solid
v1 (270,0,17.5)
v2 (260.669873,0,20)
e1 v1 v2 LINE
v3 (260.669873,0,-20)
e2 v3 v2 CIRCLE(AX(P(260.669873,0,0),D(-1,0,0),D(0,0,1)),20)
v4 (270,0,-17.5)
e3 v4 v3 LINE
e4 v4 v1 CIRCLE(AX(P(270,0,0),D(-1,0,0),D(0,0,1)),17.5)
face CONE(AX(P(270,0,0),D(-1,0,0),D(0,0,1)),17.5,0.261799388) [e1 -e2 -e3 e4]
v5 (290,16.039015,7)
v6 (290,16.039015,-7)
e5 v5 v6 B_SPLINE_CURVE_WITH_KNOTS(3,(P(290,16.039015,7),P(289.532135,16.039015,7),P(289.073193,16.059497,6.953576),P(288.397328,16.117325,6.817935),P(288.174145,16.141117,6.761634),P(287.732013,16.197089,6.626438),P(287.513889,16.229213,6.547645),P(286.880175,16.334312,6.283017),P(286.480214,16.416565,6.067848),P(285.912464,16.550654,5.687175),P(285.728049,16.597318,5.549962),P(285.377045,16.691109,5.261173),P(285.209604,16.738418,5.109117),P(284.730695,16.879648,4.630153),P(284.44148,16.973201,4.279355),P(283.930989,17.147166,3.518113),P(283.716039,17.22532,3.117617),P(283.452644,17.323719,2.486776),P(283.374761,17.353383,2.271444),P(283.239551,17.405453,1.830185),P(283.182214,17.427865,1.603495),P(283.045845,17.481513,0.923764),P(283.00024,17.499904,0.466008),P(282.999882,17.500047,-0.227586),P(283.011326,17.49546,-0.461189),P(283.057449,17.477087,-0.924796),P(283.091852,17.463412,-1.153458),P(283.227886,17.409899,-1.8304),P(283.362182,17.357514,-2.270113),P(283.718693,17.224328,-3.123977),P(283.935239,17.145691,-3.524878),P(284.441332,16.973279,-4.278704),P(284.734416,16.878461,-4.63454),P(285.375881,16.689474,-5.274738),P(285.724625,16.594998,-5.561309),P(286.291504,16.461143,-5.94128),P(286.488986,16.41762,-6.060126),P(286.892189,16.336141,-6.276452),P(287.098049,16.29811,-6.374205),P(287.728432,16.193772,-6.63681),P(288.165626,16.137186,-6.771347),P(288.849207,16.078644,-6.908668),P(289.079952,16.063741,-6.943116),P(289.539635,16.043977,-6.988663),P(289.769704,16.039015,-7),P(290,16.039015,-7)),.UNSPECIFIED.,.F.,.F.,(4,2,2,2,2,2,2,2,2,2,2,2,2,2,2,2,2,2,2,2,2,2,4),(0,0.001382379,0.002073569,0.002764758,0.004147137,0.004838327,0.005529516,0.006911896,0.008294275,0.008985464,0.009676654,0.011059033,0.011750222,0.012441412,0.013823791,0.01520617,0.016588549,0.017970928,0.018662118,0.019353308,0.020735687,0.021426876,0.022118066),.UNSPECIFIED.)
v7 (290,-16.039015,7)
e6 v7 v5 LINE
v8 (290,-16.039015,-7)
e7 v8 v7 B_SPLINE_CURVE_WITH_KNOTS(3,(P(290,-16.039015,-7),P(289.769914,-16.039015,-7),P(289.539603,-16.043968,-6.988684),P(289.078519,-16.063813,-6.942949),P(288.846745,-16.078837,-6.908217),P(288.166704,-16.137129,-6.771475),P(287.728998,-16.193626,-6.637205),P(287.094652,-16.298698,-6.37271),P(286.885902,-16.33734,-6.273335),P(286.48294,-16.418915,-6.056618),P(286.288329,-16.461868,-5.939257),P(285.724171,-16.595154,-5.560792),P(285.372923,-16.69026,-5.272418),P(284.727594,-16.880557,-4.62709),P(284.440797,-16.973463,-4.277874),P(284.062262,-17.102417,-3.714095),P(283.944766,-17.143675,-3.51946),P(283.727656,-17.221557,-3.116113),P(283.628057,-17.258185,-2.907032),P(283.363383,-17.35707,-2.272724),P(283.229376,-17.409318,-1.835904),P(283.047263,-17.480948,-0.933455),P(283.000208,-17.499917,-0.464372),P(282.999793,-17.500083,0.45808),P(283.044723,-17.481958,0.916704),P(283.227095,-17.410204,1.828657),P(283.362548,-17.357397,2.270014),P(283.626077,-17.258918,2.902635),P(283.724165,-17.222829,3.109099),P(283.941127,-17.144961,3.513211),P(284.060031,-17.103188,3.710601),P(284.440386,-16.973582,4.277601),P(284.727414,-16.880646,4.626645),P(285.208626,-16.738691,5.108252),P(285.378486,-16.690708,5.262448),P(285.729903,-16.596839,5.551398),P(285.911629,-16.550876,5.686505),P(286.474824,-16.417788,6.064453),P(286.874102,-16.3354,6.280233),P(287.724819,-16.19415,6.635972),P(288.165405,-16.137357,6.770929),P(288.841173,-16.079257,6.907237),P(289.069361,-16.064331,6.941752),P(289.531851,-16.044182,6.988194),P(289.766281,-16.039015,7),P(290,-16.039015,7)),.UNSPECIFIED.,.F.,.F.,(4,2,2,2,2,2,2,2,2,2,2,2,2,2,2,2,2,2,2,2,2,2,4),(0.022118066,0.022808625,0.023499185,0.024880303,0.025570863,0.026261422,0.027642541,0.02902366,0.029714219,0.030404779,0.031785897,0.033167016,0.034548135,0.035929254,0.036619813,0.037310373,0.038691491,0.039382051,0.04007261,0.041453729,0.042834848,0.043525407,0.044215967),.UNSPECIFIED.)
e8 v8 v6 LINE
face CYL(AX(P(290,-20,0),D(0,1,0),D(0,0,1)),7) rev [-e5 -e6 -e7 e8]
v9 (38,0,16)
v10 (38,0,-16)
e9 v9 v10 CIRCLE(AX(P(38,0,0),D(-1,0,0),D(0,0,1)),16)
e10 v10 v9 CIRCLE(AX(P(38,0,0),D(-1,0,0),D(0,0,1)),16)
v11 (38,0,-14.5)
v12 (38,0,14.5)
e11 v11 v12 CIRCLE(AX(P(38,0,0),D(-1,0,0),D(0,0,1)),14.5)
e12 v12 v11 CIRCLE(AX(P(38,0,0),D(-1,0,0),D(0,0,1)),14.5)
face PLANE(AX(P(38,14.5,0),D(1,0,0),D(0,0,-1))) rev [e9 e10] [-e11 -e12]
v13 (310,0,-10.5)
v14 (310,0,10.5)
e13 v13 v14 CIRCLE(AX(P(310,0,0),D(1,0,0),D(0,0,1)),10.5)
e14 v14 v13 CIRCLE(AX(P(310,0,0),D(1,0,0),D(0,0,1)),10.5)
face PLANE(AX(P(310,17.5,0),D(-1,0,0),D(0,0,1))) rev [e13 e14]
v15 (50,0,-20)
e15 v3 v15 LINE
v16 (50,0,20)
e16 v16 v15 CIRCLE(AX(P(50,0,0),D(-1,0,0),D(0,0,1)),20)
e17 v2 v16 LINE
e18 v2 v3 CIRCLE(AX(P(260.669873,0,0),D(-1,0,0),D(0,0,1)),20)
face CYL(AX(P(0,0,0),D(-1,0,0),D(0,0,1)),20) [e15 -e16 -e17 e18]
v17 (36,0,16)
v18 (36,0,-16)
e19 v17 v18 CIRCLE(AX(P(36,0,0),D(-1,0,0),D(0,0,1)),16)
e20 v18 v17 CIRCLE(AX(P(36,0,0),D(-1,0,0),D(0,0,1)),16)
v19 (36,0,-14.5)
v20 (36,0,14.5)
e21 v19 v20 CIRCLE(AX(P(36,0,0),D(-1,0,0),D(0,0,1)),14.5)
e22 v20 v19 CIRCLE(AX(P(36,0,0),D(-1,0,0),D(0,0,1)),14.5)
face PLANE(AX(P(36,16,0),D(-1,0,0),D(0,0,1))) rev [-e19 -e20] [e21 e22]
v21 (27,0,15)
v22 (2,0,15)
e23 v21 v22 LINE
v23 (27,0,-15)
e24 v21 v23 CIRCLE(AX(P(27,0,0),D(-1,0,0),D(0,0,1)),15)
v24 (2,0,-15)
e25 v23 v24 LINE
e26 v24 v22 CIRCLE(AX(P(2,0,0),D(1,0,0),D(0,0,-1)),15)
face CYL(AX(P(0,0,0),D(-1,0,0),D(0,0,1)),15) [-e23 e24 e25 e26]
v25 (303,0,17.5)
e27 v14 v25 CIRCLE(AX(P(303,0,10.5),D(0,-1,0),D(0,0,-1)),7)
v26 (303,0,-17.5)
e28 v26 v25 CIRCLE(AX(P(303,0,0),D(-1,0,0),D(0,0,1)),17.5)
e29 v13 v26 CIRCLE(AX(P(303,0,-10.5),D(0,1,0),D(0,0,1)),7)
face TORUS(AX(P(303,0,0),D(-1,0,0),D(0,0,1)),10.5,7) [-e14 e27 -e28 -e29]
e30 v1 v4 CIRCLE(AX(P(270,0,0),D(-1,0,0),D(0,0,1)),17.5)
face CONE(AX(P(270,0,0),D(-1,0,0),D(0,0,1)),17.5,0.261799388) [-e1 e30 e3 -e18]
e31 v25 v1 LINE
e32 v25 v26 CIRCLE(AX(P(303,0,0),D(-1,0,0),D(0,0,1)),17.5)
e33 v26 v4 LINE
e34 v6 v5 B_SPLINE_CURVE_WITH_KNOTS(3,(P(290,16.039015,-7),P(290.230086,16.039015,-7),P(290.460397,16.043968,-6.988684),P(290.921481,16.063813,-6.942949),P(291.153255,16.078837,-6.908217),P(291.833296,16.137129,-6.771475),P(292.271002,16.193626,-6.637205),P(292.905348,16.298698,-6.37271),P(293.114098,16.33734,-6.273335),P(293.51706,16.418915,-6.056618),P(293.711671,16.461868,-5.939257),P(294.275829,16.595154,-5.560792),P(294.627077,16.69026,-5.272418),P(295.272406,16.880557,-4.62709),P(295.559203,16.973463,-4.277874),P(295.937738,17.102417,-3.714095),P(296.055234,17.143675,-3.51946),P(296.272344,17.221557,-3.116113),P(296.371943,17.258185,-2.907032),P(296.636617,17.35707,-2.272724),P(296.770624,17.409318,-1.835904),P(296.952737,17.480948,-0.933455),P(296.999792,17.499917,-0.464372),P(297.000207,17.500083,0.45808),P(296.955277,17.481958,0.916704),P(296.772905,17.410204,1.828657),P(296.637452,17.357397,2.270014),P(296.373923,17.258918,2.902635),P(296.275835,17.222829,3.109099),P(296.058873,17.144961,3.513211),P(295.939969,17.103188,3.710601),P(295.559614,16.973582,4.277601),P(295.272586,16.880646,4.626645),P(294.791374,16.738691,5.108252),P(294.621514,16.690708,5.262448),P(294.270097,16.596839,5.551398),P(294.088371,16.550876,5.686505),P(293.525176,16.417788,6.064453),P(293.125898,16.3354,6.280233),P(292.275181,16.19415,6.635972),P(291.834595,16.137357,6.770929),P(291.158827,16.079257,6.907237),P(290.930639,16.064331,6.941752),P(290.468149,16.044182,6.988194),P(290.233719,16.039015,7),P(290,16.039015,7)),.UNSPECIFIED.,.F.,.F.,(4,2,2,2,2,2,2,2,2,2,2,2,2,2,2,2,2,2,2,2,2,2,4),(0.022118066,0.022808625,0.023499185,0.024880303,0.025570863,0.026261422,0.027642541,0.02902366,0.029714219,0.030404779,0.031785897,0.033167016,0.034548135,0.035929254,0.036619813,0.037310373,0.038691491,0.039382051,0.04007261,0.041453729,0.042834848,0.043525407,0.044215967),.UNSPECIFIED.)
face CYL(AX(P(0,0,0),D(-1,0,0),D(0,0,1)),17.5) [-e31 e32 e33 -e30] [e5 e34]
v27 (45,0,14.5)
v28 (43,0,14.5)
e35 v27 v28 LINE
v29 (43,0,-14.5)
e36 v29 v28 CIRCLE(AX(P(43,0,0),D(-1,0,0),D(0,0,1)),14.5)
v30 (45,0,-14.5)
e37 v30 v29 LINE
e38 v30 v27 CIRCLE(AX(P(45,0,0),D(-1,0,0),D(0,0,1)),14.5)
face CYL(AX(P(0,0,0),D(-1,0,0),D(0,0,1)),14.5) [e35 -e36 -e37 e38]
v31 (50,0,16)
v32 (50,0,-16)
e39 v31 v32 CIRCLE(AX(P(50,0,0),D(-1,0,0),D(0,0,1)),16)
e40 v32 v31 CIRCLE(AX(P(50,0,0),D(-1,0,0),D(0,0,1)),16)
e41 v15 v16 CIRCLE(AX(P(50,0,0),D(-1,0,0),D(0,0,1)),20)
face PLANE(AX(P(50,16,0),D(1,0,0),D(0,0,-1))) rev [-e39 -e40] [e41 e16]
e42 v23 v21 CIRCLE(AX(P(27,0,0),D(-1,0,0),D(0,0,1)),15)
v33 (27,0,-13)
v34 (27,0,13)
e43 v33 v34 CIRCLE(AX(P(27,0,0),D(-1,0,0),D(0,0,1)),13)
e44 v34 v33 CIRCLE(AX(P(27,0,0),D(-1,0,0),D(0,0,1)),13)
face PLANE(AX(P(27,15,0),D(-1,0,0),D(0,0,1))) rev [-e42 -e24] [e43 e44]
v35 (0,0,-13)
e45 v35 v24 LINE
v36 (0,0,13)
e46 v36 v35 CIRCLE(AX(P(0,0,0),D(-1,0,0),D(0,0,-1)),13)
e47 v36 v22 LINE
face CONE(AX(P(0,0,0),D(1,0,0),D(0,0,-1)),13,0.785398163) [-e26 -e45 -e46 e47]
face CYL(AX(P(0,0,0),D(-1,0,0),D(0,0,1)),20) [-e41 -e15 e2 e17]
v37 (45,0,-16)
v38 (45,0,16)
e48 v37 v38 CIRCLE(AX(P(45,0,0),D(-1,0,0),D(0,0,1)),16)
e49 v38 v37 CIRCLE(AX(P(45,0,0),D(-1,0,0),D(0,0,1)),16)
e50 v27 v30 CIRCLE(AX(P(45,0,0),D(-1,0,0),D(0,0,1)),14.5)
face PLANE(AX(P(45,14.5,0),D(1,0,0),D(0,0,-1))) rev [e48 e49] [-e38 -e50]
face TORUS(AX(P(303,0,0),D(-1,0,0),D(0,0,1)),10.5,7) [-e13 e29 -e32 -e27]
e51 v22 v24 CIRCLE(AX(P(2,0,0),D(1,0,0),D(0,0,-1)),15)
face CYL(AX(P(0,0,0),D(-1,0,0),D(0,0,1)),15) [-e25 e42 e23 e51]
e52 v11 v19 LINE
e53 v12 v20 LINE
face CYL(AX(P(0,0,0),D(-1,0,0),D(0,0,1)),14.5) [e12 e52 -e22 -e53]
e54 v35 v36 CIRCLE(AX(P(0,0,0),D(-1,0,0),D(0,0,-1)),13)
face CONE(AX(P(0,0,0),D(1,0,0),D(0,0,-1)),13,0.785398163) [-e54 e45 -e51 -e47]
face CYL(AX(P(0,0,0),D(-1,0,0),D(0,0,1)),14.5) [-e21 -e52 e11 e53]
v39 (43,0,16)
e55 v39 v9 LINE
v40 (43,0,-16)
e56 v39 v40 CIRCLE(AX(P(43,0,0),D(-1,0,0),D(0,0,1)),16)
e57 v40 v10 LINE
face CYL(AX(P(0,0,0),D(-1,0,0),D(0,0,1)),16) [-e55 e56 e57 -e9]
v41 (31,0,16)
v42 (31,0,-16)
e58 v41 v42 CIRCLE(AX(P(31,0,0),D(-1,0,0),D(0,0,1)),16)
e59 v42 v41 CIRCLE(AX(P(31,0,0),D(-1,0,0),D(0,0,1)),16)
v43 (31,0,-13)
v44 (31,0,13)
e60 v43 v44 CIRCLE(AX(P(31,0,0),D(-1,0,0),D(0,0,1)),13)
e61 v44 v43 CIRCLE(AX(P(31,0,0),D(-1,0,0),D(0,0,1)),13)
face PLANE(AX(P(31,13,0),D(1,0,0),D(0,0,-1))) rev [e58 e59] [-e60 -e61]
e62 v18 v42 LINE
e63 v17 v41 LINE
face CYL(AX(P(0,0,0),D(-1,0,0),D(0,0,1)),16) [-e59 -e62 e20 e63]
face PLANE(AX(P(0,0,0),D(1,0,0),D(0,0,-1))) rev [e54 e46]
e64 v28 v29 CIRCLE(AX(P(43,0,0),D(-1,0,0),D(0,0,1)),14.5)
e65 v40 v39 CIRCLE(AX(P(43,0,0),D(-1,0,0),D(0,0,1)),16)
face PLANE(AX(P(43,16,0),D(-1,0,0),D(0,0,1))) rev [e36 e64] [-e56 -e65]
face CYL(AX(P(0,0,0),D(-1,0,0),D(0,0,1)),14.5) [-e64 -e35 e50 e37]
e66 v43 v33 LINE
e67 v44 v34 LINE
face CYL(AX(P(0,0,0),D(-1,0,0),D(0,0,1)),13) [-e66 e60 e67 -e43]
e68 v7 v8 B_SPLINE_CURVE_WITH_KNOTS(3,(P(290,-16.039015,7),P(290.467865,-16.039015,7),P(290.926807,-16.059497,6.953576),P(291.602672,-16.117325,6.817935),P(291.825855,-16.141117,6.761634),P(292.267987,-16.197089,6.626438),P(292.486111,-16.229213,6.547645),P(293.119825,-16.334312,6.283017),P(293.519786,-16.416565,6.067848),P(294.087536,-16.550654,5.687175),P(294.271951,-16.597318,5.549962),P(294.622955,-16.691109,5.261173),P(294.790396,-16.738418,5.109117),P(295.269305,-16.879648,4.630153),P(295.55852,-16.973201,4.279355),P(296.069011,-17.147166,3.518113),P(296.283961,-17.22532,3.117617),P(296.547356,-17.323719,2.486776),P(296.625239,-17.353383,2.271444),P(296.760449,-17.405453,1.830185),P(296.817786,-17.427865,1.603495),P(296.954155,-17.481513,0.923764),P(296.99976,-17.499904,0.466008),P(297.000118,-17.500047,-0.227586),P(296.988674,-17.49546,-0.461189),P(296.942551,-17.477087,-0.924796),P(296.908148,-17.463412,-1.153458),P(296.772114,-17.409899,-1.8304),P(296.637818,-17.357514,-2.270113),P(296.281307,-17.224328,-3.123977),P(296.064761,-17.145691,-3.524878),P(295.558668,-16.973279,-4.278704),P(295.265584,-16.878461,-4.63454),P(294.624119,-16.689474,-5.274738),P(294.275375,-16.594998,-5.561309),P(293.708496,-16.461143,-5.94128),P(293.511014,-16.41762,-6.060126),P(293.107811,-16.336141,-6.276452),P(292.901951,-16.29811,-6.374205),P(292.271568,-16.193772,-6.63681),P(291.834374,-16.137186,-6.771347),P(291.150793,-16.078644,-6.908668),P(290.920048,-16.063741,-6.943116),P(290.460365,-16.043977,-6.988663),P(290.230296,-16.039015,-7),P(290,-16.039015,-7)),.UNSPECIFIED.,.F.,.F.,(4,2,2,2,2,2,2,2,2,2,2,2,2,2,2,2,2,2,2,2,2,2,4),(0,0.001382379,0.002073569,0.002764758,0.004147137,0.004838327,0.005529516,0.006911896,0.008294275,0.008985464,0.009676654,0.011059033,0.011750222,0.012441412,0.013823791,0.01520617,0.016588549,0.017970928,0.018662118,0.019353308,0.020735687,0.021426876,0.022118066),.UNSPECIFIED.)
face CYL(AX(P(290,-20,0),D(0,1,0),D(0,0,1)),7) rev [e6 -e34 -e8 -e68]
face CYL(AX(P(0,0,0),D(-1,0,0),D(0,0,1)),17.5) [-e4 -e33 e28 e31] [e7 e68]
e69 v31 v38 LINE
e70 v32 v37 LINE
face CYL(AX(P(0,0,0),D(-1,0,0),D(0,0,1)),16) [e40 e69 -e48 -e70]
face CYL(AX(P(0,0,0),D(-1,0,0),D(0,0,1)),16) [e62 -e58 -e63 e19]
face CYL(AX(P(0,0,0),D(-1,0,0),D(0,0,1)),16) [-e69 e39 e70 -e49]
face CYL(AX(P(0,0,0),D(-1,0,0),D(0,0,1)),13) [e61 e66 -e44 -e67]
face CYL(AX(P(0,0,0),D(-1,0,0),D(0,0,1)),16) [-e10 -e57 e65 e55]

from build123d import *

# Parameters (mm, degrees)
CUT_EXTRUDE_1_DEPTH      = 312.287648325
CUT_EXTRUDE_1_DEPTH_BACK = 312.287648325
SKETCH_2_R               = 7
CHAMFER_1_SIZE           = 2
FILLET_1_R               = 7


with BuildPart() as part:
    # 草图1 → 旋转1 (revolve)
    with BuildSketch(Plane.XY, mode=Mode.PRIVATE) as revolve_1_sk:
        Polygon((0, 0), (0, 15), (27, 15), (27, 13), (31, 13), (31, 16), (36, 16), (36, 14.5), (38, 14.5), (38, 16), (43, 16), (43, 14.5), (45, 14.5), (45, 16), (50, 16), (50, 20), (260.669872981, 20), (270, 17.5), (310, 17.5), (310, 0), align=None)
    revolve(revolve_1_sk.sketch.rotate(Axis((0, 0, 0), (1, 0, 0)), 90), axis=Axis((0, 0, 0), (1, 0, 0)))

    # 草图2 → 切除-拉伸1 (cut, two sides: drawn at the far end of the back side and taken through both)
    with BuildSketch(Plane(origin=(0, 0, 0), x_dir=(1, 0, 0), z_dir=(0, 1, 0)).offset(-CUT_EXTRUDE_1_DEPTH_BACK)):
        with Locations(Location((290, 0, 0), (0, 0, 270))):
            Circle(SKETCH_2_R)
    extrude(amount=CUT_EXTRUDE_1_DEPTH + CUT_EXTRUDE_1_DEPTH_BACK, mode=Mode.SUBTRACT)

    # 倒角1
    chamfer_1_edges = [part.edges().sort_by_distance(p)[0] for p in [
        (0, 0, -15),
    ]]
    chamfer(chamfer_1_edges, length=CHAMFER_1_SIZE)

    # 圆角1
    fillet_1_edges = [part.edges().sort_by_distance(p)[0] for p in [
        (310, 0, -17.5),
    ]]
    fillet(fillet_1_edges, radius=FILLET_1_R)


solid = part.part
